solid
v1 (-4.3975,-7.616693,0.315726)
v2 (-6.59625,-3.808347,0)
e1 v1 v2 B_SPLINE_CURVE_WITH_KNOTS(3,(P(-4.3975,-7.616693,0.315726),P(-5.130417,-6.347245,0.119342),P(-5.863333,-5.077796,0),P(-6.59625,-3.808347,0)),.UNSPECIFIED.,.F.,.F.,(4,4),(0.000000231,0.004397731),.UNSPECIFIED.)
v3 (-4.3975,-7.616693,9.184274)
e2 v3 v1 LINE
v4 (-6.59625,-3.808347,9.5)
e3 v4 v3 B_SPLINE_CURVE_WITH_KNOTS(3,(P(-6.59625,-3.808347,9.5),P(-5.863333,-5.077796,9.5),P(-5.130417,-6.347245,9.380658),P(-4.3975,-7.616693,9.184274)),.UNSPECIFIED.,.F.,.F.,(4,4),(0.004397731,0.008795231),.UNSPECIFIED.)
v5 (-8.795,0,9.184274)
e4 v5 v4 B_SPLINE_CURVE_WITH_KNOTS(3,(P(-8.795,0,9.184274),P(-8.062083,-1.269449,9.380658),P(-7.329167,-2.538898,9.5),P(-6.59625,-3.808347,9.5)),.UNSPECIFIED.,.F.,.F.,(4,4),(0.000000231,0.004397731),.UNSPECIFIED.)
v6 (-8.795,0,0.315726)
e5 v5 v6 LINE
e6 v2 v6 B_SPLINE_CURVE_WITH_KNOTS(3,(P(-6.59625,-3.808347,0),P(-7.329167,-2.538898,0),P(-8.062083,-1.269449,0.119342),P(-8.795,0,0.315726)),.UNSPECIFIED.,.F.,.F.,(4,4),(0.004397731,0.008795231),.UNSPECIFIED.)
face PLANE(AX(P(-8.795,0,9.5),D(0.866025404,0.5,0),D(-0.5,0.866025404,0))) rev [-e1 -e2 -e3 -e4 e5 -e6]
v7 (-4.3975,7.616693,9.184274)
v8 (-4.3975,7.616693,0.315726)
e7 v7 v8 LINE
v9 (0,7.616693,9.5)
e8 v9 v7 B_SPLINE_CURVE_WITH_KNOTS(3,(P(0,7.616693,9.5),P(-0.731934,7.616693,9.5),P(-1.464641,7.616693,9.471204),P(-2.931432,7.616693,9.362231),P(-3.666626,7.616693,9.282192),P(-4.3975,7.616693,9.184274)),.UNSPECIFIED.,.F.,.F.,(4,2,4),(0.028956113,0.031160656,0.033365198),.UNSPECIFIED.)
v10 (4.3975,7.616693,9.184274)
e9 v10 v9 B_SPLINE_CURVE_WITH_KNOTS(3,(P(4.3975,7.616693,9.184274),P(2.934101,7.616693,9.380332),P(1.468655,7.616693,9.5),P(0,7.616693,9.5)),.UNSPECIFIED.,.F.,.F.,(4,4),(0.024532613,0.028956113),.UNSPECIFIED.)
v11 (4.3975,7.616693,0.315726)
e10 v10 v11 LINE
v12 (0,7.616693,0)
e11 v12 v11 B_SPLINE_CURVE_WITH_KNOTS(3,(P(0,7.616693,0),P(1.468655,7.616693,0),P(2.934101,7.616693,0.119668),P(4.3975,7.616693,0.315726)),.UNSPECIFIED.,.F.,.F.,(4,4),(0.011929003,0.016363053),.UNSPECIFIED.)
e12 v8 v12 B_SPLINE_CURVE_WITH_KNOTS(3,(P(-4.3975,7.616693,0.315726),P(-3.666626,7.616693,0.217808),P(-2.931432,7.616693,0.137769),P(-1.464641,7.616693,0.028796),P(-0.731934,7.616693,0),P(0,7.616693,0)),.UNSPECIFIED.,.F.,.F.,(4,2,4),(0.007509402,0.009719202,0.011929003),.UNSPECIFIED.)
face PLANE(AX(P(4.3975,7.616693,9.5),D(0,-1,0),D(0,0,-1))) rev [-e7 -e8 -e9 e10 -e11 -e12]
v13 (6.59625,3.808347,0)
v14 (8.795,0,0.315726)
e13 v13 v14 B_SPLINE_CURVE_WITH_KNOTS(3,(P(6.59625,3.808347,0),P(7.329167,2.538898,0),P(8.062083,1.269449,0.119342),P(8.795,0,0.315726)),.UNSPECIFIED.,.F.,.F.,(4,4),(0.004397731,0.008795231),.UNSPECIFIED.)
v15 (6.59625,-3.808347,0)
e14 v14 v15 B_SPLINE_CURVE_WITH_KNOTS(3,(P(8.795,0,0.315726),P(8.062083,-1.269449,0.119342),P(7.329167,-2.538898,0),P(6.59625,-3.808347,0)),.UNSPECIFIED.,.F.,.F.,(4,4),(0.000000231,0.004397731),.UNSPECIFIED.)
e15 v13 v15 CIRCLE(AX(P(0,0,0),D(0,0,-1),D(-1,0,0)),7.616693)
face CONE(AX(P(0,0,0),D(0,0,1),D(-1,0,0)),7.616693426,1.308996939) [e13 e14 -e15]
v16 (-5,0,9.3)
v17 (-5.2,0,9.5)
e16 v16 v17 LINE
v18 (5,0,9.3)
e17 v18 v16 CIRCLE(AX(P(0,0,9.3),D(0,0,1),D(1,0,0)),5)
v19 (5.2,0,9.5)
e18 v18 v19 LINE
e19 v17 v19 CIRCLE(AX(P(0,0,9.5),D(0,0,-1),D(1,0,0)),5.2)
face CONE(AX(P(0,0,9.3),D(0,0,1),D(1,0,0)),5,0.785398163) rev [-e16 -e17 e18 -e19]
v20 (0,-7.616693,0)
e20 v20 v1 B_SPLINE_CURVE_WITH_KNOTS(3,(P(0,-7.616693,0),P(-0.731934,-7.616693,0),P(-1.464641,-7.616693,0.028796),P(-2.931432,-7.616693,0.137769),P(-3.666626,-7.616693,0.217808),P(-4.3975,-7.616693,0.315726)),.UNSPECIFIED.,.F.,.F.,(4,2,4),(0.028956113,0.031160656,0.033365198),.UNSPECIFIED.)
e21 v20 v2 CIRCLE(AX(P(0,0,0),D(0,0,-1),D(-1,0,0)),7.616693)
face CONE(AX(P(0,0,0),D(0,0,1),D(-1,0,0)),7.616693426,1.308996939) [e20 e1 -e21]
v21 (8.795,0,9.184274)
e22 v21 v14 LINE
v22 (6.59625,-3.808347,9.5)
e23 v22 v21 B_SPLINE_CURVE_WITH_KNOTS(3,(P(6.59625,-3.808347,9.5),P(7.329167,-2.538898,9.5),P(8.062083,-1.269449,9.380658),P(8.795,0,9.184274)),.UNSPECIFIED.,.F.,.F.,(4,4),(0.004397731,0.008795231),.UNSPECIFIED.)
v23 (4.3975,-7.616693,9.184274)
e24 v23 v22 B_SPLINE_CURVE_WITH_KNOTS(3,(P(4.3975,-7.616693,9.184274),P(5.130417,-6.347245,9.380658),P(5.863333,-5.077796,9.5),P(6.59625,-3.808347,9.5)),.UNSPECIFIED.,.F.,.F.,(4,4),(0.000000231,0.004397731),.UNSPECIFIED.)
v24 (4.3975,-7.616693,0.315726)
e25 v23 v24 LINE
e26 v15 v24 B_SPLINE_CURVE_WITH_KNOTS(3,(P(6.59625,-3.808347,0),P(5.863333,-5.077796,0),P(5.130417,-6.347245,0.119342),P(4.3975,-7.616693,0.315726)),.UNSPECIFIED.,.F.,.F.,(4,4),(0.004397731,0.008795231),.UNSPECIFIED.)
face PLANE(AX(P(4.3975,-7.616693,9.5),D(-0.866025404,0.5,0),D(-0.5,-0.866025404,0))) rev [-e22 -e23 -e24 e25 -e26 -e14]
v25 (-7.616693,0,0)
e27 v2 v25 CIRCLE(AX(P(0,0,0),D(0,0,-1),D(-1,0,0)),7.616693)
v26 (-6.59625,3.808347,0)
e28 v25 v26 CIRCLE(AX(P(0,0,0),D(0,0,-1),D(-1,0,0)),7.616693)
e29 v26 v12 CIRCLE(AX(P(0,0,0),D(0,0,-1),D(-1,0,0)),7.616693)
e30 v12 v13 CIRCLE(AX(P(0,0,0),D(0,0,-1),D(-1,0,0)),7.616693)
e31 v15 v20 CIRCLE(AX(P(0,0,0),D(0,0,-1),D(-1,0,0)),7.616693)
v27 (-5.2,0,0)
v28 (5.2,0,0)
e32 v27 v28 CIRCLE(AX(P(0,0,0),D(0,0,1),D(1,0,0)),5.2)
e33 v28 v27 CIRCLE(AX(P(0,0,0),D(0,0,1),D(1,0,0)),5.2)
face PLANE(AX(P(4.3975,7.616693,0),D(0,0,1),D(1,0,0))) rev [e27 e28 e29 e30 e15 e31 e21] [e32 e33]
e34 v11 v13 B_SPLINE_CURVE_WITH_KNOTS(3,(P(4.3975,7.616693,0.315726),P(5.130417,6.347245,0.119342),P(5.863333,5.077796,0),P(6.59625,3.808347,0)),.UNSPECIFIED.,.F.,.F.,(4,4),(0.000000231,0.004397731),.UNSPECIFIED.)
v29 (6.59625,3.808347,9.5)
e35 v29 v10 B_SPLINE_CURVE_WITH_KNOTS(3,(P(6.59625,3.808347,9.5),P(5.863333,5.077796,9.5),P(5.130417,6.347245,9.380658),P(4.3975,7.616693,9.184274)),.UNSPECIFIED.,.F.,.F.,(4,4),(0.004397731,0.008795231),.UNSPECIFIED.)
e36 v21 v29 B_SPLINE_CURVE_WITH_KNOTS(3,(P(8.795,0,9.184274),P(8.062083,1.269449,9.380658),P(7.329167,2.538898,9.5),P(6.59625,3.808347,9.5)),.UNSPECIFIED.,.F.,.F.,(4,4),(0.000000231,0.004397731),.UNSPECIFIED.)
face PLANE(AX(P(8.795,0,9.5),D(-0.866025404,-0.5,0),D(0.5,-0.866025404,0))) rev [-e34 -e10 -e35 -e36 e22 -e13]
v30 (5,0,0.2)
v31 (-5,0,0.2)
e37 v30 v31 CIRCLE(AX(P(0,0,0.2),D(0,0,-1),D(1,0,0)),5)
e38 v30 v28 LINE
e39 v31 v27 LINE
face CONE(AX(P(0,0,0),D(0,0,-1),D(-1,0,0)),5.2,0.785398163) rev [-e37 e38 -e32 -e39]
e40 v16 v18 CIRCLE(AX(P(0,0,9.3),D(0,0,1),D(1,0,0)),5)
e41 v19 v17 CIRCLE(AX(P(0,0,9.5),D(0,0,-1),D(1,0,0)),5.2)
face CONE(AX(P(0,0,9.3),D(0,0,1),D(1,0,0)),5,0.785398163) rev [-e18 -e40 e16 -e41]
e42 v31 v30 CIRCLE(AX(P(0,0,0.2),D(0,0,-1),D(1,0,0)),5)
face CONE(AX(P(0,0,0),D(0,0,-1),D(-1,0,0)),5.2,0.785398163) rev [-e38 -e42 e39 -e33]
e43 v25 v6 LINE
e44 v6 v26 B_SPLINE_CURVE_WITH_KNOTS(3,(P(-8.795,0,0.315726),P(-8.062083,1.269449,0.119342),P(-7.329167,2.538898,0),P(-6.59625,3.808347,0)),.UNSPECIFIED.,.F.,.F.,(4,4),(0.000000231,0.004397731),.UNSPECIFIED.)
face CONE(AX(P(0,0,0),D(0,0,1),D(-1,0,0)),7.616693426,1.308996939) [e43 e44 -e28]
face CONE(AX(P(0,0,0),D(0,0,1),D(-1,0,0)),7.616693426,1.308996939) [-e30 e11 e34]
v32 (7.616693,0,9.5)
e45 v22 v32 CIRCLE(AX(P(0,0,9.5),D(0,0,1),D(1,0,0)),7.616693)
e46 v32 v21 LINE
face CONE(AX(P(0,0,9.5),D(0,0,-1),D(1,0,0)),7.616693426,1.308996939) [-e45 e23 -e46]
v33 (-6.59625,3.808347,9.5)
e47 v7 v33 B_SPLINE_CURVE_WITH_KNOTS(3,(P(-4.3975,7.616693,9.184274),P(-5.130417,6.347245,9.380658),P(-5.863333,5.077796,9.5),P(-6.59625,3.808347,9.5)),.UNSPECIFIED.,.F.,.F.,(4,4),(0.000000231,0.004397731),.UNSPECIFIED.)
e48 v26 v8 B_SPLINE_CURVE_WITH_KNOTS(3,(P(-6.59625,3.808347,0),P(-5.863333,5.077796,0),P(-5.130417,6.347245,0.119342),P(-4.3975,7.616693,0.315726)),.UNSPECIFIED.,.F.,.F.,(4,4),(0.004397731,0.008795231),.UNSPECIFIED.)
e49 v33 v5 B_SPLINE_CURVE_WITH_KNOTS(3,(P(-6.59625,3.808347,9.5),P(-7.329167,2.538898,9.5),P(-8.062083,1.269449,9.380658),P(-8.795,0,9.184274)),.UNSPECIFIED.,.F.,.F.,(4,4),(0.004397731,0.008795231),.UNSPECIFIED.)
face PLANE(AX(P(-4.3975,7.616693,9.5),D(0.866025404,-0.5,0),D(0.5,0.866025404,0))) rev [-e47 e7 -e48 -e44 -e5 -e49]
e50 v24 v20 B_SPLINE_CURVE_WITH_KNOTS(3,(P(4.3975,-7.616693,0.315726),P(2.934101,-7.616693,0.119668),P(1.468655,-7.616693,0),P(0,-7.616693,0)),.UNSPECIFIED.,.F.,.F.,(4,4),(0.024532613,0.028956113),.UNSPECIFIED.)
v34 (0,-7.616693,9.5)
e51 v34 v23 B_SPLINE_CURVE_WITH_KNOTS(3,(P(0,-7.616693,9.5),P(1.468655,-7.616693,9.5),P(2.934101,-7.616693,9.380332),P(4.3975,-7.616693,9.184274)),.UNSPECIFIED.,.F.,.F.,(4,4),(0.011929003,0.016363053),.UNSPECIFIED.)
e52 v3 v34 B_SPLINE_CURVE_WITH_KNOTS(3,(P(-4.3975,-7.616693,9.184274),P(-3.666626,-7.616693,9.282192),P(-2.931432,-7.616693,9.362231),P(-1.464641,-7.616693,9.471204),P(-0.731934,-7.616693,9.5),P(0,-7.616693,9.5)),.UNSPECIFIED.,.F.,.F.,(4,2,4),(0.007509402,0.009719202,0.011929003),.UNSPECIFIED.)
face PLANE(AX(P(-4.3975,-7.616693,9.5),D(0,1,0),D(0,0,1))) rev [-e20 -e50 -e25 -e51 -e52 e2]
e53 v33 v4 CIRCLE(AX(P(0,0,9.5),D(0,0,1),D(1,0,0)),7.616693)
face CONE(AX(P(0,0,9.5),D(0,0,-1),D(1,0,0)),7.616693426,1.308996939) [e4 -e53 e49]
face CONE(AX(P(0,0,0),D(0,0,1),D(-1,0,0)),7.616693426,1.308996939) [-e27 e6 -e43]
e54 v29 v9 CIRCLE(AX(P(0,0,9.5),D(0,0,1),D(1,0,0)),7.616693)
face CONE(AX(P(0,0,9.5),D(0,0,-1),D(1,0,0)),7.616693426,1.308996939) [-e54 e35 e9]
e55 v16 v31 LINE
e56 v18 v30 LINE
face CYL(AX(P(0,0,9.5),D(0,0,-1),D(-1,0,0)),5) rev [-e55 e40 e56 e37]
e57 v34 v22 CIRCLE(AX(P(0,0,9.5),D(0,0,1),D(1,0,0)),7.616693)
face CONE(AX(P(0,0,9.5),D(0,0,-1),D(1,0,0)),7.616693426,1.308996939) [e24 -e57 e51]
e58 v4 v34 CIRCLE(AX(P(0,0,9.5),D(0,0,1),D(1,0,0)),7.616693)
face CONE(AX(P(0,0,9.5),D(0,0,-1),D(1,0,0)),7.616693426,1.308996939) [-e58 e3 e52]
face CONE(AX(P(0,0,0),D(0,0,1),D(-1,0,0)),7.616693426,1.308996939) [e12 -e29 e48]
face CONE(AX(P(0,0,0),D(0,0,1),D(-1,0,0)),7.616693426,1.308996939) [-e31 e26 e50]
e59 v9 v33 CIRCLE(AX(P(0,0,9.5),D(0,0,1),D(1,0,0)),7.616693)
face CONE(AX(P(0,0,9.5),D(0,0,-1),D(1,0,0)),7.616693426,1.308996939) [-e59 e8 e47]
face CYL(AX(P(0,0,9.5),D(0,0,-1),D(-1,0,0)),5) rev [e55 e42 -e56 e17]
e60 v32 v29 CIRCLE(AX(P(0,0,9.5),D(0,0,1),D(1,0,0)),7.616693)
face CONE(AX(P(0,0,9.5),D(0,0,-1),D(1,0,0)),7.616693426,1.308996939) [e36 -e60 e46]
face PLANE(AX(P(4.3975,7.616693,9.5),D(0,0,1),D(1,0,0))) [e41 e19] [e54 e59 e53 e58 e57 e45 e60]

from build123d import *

# Parameters (mm, degrees)
SKETCH1_R          = 5
BOSS_EXTRUDE_DEPTH = 9.5
SKETCH2_OUTSIDE_W  = 308.252
SKETCH2_OUTSIDE_H  = 305.896
SKETCH2_OUTSIDE_R  = 7.616693426
CUT_EXTRUDE1_DEPTH = 38
CUT_EXTRUDE1_DRAFT = -75
SKETCH3_OUTSIDE_W  = 308.252
SKETCH3_OUTSIDE_H  = 305.896
SKETCH3_OUTSIDE_R  = 7.616693426
CUT_EXTRUDE2_DEPTH = 38
CUT_EXTRUDE2_DRAFT = -75
CHAMFER1_SIZE      = 0.2


with BuildPart() as part:
    # Sketch1 → Boss-Extrude (new body)
    with BuildSketch(Plane.XY):
        Polygon((4.3975, 7.616693426), (-4.3975, 7.616693426), (-8.795, 0), (-4.3975, -7.616693426), (4.3975, -7.616693426), (8.795, 0), align=None)
        Circle(SKETCH1_R, mode=Mode.SUBTRACT)
    extrude(amount=BOSS_EXTRUDE_DEPTH)


with BuildPart() as cut_extrude1_tool:
    # Sketch2 outside → Cut-Extrude1 (with draft: the straight prism first)
    with BuildSketch(Plane(origin=(0, 0, 0), x_dir=(-1, 0, 0), z_dir=(0, 0, -1))):
        Rectangle(SKETCH2_OUTSIDE_W, SKETCH2_OUTSIDE_H)
        Circle(SKETCH2_OUTSIDE_R, mode=Mode.SUBTRACT)
    extrude(amount=-CUT_EXTRUDE1_DEPTH)
    # Cut-Extrude1: the draft: its side faces are tilted about the plane it starts from
    cut_extrude1_sides = [cut_extrude1_tool.faces().sort_by_distance(p)[0] for p in [
        (0, -152.948, 19),
        (-154.126, 0, 19),
        (0, 152.948, 19),
        (154.126, 0, 19),
        (7.616693426, 0, 19),
    ]]
    draft(cut_extrude1_sides, Plane(origin=(0, 0, 0), x_dir=(-1, 0, 0), z_dir=(0, 0, -1)), CUT_EXTRUDE1_DRAFT)


with BuildPart() as part_1:
    add(part.part)

    # Cut-Extrude1: cut by cut_extrude1_tool
    add(cut_extrude1_tool.part, mode=Mode.SUBTRACT)


with BuildPart() as cut_extrude2_tool:
    # Sketch3 outside → Cut-Extrude2 (with draft: the straight prism first)
    with BuildSketch(Plane.XY.offset(9.5)):
        Rectangle(SKETCH3_OUTSIDE_W, SKETCH3_OUTSIDE_H)
        Circle(SKETCH3_OUTSIDE_R, mode=Mode.SUBTRACT)
    extrude(amount=-CUT_EXTRUDE2_DEPTH)
    # Cut-Extrude2: the draft: its side faces are tilted about the plane it starts from
    cut_extrude2_sides = [cut_extrude2_tool.faces().sort_by_distance(p)[0] for p in [
        (0, -152.948, -9.5),
        (154.126, 0, -9.5),
        (0, 152.948, -9.5),
        (-154.126, 0, -9.5),
        (-7.616693426, 0, -9.5),
    ]]
    draft(cut_extrude2_sides, Plane.XY.offset(9.5), CUT_EXTRUDE2_DRAFT)


with BuildPart() as part_2:
    add(part_1.part)

    # Cut-Extrude2: cut by cut_extrude2_tool
    add(cut_extrude2_tool.part, mode=Mode.SUBTRACT)

    # Chamfer1
    chamfer1_edges = [part_2.edges().sort_by_distance(p)[0] for p in [
        (-5, 0, 0),
        (-5, 0, 9.5),
    ]]
    chamfer(chamfer1_edges, length=CHAMFER1_SIZE)


solid = part_2.part
